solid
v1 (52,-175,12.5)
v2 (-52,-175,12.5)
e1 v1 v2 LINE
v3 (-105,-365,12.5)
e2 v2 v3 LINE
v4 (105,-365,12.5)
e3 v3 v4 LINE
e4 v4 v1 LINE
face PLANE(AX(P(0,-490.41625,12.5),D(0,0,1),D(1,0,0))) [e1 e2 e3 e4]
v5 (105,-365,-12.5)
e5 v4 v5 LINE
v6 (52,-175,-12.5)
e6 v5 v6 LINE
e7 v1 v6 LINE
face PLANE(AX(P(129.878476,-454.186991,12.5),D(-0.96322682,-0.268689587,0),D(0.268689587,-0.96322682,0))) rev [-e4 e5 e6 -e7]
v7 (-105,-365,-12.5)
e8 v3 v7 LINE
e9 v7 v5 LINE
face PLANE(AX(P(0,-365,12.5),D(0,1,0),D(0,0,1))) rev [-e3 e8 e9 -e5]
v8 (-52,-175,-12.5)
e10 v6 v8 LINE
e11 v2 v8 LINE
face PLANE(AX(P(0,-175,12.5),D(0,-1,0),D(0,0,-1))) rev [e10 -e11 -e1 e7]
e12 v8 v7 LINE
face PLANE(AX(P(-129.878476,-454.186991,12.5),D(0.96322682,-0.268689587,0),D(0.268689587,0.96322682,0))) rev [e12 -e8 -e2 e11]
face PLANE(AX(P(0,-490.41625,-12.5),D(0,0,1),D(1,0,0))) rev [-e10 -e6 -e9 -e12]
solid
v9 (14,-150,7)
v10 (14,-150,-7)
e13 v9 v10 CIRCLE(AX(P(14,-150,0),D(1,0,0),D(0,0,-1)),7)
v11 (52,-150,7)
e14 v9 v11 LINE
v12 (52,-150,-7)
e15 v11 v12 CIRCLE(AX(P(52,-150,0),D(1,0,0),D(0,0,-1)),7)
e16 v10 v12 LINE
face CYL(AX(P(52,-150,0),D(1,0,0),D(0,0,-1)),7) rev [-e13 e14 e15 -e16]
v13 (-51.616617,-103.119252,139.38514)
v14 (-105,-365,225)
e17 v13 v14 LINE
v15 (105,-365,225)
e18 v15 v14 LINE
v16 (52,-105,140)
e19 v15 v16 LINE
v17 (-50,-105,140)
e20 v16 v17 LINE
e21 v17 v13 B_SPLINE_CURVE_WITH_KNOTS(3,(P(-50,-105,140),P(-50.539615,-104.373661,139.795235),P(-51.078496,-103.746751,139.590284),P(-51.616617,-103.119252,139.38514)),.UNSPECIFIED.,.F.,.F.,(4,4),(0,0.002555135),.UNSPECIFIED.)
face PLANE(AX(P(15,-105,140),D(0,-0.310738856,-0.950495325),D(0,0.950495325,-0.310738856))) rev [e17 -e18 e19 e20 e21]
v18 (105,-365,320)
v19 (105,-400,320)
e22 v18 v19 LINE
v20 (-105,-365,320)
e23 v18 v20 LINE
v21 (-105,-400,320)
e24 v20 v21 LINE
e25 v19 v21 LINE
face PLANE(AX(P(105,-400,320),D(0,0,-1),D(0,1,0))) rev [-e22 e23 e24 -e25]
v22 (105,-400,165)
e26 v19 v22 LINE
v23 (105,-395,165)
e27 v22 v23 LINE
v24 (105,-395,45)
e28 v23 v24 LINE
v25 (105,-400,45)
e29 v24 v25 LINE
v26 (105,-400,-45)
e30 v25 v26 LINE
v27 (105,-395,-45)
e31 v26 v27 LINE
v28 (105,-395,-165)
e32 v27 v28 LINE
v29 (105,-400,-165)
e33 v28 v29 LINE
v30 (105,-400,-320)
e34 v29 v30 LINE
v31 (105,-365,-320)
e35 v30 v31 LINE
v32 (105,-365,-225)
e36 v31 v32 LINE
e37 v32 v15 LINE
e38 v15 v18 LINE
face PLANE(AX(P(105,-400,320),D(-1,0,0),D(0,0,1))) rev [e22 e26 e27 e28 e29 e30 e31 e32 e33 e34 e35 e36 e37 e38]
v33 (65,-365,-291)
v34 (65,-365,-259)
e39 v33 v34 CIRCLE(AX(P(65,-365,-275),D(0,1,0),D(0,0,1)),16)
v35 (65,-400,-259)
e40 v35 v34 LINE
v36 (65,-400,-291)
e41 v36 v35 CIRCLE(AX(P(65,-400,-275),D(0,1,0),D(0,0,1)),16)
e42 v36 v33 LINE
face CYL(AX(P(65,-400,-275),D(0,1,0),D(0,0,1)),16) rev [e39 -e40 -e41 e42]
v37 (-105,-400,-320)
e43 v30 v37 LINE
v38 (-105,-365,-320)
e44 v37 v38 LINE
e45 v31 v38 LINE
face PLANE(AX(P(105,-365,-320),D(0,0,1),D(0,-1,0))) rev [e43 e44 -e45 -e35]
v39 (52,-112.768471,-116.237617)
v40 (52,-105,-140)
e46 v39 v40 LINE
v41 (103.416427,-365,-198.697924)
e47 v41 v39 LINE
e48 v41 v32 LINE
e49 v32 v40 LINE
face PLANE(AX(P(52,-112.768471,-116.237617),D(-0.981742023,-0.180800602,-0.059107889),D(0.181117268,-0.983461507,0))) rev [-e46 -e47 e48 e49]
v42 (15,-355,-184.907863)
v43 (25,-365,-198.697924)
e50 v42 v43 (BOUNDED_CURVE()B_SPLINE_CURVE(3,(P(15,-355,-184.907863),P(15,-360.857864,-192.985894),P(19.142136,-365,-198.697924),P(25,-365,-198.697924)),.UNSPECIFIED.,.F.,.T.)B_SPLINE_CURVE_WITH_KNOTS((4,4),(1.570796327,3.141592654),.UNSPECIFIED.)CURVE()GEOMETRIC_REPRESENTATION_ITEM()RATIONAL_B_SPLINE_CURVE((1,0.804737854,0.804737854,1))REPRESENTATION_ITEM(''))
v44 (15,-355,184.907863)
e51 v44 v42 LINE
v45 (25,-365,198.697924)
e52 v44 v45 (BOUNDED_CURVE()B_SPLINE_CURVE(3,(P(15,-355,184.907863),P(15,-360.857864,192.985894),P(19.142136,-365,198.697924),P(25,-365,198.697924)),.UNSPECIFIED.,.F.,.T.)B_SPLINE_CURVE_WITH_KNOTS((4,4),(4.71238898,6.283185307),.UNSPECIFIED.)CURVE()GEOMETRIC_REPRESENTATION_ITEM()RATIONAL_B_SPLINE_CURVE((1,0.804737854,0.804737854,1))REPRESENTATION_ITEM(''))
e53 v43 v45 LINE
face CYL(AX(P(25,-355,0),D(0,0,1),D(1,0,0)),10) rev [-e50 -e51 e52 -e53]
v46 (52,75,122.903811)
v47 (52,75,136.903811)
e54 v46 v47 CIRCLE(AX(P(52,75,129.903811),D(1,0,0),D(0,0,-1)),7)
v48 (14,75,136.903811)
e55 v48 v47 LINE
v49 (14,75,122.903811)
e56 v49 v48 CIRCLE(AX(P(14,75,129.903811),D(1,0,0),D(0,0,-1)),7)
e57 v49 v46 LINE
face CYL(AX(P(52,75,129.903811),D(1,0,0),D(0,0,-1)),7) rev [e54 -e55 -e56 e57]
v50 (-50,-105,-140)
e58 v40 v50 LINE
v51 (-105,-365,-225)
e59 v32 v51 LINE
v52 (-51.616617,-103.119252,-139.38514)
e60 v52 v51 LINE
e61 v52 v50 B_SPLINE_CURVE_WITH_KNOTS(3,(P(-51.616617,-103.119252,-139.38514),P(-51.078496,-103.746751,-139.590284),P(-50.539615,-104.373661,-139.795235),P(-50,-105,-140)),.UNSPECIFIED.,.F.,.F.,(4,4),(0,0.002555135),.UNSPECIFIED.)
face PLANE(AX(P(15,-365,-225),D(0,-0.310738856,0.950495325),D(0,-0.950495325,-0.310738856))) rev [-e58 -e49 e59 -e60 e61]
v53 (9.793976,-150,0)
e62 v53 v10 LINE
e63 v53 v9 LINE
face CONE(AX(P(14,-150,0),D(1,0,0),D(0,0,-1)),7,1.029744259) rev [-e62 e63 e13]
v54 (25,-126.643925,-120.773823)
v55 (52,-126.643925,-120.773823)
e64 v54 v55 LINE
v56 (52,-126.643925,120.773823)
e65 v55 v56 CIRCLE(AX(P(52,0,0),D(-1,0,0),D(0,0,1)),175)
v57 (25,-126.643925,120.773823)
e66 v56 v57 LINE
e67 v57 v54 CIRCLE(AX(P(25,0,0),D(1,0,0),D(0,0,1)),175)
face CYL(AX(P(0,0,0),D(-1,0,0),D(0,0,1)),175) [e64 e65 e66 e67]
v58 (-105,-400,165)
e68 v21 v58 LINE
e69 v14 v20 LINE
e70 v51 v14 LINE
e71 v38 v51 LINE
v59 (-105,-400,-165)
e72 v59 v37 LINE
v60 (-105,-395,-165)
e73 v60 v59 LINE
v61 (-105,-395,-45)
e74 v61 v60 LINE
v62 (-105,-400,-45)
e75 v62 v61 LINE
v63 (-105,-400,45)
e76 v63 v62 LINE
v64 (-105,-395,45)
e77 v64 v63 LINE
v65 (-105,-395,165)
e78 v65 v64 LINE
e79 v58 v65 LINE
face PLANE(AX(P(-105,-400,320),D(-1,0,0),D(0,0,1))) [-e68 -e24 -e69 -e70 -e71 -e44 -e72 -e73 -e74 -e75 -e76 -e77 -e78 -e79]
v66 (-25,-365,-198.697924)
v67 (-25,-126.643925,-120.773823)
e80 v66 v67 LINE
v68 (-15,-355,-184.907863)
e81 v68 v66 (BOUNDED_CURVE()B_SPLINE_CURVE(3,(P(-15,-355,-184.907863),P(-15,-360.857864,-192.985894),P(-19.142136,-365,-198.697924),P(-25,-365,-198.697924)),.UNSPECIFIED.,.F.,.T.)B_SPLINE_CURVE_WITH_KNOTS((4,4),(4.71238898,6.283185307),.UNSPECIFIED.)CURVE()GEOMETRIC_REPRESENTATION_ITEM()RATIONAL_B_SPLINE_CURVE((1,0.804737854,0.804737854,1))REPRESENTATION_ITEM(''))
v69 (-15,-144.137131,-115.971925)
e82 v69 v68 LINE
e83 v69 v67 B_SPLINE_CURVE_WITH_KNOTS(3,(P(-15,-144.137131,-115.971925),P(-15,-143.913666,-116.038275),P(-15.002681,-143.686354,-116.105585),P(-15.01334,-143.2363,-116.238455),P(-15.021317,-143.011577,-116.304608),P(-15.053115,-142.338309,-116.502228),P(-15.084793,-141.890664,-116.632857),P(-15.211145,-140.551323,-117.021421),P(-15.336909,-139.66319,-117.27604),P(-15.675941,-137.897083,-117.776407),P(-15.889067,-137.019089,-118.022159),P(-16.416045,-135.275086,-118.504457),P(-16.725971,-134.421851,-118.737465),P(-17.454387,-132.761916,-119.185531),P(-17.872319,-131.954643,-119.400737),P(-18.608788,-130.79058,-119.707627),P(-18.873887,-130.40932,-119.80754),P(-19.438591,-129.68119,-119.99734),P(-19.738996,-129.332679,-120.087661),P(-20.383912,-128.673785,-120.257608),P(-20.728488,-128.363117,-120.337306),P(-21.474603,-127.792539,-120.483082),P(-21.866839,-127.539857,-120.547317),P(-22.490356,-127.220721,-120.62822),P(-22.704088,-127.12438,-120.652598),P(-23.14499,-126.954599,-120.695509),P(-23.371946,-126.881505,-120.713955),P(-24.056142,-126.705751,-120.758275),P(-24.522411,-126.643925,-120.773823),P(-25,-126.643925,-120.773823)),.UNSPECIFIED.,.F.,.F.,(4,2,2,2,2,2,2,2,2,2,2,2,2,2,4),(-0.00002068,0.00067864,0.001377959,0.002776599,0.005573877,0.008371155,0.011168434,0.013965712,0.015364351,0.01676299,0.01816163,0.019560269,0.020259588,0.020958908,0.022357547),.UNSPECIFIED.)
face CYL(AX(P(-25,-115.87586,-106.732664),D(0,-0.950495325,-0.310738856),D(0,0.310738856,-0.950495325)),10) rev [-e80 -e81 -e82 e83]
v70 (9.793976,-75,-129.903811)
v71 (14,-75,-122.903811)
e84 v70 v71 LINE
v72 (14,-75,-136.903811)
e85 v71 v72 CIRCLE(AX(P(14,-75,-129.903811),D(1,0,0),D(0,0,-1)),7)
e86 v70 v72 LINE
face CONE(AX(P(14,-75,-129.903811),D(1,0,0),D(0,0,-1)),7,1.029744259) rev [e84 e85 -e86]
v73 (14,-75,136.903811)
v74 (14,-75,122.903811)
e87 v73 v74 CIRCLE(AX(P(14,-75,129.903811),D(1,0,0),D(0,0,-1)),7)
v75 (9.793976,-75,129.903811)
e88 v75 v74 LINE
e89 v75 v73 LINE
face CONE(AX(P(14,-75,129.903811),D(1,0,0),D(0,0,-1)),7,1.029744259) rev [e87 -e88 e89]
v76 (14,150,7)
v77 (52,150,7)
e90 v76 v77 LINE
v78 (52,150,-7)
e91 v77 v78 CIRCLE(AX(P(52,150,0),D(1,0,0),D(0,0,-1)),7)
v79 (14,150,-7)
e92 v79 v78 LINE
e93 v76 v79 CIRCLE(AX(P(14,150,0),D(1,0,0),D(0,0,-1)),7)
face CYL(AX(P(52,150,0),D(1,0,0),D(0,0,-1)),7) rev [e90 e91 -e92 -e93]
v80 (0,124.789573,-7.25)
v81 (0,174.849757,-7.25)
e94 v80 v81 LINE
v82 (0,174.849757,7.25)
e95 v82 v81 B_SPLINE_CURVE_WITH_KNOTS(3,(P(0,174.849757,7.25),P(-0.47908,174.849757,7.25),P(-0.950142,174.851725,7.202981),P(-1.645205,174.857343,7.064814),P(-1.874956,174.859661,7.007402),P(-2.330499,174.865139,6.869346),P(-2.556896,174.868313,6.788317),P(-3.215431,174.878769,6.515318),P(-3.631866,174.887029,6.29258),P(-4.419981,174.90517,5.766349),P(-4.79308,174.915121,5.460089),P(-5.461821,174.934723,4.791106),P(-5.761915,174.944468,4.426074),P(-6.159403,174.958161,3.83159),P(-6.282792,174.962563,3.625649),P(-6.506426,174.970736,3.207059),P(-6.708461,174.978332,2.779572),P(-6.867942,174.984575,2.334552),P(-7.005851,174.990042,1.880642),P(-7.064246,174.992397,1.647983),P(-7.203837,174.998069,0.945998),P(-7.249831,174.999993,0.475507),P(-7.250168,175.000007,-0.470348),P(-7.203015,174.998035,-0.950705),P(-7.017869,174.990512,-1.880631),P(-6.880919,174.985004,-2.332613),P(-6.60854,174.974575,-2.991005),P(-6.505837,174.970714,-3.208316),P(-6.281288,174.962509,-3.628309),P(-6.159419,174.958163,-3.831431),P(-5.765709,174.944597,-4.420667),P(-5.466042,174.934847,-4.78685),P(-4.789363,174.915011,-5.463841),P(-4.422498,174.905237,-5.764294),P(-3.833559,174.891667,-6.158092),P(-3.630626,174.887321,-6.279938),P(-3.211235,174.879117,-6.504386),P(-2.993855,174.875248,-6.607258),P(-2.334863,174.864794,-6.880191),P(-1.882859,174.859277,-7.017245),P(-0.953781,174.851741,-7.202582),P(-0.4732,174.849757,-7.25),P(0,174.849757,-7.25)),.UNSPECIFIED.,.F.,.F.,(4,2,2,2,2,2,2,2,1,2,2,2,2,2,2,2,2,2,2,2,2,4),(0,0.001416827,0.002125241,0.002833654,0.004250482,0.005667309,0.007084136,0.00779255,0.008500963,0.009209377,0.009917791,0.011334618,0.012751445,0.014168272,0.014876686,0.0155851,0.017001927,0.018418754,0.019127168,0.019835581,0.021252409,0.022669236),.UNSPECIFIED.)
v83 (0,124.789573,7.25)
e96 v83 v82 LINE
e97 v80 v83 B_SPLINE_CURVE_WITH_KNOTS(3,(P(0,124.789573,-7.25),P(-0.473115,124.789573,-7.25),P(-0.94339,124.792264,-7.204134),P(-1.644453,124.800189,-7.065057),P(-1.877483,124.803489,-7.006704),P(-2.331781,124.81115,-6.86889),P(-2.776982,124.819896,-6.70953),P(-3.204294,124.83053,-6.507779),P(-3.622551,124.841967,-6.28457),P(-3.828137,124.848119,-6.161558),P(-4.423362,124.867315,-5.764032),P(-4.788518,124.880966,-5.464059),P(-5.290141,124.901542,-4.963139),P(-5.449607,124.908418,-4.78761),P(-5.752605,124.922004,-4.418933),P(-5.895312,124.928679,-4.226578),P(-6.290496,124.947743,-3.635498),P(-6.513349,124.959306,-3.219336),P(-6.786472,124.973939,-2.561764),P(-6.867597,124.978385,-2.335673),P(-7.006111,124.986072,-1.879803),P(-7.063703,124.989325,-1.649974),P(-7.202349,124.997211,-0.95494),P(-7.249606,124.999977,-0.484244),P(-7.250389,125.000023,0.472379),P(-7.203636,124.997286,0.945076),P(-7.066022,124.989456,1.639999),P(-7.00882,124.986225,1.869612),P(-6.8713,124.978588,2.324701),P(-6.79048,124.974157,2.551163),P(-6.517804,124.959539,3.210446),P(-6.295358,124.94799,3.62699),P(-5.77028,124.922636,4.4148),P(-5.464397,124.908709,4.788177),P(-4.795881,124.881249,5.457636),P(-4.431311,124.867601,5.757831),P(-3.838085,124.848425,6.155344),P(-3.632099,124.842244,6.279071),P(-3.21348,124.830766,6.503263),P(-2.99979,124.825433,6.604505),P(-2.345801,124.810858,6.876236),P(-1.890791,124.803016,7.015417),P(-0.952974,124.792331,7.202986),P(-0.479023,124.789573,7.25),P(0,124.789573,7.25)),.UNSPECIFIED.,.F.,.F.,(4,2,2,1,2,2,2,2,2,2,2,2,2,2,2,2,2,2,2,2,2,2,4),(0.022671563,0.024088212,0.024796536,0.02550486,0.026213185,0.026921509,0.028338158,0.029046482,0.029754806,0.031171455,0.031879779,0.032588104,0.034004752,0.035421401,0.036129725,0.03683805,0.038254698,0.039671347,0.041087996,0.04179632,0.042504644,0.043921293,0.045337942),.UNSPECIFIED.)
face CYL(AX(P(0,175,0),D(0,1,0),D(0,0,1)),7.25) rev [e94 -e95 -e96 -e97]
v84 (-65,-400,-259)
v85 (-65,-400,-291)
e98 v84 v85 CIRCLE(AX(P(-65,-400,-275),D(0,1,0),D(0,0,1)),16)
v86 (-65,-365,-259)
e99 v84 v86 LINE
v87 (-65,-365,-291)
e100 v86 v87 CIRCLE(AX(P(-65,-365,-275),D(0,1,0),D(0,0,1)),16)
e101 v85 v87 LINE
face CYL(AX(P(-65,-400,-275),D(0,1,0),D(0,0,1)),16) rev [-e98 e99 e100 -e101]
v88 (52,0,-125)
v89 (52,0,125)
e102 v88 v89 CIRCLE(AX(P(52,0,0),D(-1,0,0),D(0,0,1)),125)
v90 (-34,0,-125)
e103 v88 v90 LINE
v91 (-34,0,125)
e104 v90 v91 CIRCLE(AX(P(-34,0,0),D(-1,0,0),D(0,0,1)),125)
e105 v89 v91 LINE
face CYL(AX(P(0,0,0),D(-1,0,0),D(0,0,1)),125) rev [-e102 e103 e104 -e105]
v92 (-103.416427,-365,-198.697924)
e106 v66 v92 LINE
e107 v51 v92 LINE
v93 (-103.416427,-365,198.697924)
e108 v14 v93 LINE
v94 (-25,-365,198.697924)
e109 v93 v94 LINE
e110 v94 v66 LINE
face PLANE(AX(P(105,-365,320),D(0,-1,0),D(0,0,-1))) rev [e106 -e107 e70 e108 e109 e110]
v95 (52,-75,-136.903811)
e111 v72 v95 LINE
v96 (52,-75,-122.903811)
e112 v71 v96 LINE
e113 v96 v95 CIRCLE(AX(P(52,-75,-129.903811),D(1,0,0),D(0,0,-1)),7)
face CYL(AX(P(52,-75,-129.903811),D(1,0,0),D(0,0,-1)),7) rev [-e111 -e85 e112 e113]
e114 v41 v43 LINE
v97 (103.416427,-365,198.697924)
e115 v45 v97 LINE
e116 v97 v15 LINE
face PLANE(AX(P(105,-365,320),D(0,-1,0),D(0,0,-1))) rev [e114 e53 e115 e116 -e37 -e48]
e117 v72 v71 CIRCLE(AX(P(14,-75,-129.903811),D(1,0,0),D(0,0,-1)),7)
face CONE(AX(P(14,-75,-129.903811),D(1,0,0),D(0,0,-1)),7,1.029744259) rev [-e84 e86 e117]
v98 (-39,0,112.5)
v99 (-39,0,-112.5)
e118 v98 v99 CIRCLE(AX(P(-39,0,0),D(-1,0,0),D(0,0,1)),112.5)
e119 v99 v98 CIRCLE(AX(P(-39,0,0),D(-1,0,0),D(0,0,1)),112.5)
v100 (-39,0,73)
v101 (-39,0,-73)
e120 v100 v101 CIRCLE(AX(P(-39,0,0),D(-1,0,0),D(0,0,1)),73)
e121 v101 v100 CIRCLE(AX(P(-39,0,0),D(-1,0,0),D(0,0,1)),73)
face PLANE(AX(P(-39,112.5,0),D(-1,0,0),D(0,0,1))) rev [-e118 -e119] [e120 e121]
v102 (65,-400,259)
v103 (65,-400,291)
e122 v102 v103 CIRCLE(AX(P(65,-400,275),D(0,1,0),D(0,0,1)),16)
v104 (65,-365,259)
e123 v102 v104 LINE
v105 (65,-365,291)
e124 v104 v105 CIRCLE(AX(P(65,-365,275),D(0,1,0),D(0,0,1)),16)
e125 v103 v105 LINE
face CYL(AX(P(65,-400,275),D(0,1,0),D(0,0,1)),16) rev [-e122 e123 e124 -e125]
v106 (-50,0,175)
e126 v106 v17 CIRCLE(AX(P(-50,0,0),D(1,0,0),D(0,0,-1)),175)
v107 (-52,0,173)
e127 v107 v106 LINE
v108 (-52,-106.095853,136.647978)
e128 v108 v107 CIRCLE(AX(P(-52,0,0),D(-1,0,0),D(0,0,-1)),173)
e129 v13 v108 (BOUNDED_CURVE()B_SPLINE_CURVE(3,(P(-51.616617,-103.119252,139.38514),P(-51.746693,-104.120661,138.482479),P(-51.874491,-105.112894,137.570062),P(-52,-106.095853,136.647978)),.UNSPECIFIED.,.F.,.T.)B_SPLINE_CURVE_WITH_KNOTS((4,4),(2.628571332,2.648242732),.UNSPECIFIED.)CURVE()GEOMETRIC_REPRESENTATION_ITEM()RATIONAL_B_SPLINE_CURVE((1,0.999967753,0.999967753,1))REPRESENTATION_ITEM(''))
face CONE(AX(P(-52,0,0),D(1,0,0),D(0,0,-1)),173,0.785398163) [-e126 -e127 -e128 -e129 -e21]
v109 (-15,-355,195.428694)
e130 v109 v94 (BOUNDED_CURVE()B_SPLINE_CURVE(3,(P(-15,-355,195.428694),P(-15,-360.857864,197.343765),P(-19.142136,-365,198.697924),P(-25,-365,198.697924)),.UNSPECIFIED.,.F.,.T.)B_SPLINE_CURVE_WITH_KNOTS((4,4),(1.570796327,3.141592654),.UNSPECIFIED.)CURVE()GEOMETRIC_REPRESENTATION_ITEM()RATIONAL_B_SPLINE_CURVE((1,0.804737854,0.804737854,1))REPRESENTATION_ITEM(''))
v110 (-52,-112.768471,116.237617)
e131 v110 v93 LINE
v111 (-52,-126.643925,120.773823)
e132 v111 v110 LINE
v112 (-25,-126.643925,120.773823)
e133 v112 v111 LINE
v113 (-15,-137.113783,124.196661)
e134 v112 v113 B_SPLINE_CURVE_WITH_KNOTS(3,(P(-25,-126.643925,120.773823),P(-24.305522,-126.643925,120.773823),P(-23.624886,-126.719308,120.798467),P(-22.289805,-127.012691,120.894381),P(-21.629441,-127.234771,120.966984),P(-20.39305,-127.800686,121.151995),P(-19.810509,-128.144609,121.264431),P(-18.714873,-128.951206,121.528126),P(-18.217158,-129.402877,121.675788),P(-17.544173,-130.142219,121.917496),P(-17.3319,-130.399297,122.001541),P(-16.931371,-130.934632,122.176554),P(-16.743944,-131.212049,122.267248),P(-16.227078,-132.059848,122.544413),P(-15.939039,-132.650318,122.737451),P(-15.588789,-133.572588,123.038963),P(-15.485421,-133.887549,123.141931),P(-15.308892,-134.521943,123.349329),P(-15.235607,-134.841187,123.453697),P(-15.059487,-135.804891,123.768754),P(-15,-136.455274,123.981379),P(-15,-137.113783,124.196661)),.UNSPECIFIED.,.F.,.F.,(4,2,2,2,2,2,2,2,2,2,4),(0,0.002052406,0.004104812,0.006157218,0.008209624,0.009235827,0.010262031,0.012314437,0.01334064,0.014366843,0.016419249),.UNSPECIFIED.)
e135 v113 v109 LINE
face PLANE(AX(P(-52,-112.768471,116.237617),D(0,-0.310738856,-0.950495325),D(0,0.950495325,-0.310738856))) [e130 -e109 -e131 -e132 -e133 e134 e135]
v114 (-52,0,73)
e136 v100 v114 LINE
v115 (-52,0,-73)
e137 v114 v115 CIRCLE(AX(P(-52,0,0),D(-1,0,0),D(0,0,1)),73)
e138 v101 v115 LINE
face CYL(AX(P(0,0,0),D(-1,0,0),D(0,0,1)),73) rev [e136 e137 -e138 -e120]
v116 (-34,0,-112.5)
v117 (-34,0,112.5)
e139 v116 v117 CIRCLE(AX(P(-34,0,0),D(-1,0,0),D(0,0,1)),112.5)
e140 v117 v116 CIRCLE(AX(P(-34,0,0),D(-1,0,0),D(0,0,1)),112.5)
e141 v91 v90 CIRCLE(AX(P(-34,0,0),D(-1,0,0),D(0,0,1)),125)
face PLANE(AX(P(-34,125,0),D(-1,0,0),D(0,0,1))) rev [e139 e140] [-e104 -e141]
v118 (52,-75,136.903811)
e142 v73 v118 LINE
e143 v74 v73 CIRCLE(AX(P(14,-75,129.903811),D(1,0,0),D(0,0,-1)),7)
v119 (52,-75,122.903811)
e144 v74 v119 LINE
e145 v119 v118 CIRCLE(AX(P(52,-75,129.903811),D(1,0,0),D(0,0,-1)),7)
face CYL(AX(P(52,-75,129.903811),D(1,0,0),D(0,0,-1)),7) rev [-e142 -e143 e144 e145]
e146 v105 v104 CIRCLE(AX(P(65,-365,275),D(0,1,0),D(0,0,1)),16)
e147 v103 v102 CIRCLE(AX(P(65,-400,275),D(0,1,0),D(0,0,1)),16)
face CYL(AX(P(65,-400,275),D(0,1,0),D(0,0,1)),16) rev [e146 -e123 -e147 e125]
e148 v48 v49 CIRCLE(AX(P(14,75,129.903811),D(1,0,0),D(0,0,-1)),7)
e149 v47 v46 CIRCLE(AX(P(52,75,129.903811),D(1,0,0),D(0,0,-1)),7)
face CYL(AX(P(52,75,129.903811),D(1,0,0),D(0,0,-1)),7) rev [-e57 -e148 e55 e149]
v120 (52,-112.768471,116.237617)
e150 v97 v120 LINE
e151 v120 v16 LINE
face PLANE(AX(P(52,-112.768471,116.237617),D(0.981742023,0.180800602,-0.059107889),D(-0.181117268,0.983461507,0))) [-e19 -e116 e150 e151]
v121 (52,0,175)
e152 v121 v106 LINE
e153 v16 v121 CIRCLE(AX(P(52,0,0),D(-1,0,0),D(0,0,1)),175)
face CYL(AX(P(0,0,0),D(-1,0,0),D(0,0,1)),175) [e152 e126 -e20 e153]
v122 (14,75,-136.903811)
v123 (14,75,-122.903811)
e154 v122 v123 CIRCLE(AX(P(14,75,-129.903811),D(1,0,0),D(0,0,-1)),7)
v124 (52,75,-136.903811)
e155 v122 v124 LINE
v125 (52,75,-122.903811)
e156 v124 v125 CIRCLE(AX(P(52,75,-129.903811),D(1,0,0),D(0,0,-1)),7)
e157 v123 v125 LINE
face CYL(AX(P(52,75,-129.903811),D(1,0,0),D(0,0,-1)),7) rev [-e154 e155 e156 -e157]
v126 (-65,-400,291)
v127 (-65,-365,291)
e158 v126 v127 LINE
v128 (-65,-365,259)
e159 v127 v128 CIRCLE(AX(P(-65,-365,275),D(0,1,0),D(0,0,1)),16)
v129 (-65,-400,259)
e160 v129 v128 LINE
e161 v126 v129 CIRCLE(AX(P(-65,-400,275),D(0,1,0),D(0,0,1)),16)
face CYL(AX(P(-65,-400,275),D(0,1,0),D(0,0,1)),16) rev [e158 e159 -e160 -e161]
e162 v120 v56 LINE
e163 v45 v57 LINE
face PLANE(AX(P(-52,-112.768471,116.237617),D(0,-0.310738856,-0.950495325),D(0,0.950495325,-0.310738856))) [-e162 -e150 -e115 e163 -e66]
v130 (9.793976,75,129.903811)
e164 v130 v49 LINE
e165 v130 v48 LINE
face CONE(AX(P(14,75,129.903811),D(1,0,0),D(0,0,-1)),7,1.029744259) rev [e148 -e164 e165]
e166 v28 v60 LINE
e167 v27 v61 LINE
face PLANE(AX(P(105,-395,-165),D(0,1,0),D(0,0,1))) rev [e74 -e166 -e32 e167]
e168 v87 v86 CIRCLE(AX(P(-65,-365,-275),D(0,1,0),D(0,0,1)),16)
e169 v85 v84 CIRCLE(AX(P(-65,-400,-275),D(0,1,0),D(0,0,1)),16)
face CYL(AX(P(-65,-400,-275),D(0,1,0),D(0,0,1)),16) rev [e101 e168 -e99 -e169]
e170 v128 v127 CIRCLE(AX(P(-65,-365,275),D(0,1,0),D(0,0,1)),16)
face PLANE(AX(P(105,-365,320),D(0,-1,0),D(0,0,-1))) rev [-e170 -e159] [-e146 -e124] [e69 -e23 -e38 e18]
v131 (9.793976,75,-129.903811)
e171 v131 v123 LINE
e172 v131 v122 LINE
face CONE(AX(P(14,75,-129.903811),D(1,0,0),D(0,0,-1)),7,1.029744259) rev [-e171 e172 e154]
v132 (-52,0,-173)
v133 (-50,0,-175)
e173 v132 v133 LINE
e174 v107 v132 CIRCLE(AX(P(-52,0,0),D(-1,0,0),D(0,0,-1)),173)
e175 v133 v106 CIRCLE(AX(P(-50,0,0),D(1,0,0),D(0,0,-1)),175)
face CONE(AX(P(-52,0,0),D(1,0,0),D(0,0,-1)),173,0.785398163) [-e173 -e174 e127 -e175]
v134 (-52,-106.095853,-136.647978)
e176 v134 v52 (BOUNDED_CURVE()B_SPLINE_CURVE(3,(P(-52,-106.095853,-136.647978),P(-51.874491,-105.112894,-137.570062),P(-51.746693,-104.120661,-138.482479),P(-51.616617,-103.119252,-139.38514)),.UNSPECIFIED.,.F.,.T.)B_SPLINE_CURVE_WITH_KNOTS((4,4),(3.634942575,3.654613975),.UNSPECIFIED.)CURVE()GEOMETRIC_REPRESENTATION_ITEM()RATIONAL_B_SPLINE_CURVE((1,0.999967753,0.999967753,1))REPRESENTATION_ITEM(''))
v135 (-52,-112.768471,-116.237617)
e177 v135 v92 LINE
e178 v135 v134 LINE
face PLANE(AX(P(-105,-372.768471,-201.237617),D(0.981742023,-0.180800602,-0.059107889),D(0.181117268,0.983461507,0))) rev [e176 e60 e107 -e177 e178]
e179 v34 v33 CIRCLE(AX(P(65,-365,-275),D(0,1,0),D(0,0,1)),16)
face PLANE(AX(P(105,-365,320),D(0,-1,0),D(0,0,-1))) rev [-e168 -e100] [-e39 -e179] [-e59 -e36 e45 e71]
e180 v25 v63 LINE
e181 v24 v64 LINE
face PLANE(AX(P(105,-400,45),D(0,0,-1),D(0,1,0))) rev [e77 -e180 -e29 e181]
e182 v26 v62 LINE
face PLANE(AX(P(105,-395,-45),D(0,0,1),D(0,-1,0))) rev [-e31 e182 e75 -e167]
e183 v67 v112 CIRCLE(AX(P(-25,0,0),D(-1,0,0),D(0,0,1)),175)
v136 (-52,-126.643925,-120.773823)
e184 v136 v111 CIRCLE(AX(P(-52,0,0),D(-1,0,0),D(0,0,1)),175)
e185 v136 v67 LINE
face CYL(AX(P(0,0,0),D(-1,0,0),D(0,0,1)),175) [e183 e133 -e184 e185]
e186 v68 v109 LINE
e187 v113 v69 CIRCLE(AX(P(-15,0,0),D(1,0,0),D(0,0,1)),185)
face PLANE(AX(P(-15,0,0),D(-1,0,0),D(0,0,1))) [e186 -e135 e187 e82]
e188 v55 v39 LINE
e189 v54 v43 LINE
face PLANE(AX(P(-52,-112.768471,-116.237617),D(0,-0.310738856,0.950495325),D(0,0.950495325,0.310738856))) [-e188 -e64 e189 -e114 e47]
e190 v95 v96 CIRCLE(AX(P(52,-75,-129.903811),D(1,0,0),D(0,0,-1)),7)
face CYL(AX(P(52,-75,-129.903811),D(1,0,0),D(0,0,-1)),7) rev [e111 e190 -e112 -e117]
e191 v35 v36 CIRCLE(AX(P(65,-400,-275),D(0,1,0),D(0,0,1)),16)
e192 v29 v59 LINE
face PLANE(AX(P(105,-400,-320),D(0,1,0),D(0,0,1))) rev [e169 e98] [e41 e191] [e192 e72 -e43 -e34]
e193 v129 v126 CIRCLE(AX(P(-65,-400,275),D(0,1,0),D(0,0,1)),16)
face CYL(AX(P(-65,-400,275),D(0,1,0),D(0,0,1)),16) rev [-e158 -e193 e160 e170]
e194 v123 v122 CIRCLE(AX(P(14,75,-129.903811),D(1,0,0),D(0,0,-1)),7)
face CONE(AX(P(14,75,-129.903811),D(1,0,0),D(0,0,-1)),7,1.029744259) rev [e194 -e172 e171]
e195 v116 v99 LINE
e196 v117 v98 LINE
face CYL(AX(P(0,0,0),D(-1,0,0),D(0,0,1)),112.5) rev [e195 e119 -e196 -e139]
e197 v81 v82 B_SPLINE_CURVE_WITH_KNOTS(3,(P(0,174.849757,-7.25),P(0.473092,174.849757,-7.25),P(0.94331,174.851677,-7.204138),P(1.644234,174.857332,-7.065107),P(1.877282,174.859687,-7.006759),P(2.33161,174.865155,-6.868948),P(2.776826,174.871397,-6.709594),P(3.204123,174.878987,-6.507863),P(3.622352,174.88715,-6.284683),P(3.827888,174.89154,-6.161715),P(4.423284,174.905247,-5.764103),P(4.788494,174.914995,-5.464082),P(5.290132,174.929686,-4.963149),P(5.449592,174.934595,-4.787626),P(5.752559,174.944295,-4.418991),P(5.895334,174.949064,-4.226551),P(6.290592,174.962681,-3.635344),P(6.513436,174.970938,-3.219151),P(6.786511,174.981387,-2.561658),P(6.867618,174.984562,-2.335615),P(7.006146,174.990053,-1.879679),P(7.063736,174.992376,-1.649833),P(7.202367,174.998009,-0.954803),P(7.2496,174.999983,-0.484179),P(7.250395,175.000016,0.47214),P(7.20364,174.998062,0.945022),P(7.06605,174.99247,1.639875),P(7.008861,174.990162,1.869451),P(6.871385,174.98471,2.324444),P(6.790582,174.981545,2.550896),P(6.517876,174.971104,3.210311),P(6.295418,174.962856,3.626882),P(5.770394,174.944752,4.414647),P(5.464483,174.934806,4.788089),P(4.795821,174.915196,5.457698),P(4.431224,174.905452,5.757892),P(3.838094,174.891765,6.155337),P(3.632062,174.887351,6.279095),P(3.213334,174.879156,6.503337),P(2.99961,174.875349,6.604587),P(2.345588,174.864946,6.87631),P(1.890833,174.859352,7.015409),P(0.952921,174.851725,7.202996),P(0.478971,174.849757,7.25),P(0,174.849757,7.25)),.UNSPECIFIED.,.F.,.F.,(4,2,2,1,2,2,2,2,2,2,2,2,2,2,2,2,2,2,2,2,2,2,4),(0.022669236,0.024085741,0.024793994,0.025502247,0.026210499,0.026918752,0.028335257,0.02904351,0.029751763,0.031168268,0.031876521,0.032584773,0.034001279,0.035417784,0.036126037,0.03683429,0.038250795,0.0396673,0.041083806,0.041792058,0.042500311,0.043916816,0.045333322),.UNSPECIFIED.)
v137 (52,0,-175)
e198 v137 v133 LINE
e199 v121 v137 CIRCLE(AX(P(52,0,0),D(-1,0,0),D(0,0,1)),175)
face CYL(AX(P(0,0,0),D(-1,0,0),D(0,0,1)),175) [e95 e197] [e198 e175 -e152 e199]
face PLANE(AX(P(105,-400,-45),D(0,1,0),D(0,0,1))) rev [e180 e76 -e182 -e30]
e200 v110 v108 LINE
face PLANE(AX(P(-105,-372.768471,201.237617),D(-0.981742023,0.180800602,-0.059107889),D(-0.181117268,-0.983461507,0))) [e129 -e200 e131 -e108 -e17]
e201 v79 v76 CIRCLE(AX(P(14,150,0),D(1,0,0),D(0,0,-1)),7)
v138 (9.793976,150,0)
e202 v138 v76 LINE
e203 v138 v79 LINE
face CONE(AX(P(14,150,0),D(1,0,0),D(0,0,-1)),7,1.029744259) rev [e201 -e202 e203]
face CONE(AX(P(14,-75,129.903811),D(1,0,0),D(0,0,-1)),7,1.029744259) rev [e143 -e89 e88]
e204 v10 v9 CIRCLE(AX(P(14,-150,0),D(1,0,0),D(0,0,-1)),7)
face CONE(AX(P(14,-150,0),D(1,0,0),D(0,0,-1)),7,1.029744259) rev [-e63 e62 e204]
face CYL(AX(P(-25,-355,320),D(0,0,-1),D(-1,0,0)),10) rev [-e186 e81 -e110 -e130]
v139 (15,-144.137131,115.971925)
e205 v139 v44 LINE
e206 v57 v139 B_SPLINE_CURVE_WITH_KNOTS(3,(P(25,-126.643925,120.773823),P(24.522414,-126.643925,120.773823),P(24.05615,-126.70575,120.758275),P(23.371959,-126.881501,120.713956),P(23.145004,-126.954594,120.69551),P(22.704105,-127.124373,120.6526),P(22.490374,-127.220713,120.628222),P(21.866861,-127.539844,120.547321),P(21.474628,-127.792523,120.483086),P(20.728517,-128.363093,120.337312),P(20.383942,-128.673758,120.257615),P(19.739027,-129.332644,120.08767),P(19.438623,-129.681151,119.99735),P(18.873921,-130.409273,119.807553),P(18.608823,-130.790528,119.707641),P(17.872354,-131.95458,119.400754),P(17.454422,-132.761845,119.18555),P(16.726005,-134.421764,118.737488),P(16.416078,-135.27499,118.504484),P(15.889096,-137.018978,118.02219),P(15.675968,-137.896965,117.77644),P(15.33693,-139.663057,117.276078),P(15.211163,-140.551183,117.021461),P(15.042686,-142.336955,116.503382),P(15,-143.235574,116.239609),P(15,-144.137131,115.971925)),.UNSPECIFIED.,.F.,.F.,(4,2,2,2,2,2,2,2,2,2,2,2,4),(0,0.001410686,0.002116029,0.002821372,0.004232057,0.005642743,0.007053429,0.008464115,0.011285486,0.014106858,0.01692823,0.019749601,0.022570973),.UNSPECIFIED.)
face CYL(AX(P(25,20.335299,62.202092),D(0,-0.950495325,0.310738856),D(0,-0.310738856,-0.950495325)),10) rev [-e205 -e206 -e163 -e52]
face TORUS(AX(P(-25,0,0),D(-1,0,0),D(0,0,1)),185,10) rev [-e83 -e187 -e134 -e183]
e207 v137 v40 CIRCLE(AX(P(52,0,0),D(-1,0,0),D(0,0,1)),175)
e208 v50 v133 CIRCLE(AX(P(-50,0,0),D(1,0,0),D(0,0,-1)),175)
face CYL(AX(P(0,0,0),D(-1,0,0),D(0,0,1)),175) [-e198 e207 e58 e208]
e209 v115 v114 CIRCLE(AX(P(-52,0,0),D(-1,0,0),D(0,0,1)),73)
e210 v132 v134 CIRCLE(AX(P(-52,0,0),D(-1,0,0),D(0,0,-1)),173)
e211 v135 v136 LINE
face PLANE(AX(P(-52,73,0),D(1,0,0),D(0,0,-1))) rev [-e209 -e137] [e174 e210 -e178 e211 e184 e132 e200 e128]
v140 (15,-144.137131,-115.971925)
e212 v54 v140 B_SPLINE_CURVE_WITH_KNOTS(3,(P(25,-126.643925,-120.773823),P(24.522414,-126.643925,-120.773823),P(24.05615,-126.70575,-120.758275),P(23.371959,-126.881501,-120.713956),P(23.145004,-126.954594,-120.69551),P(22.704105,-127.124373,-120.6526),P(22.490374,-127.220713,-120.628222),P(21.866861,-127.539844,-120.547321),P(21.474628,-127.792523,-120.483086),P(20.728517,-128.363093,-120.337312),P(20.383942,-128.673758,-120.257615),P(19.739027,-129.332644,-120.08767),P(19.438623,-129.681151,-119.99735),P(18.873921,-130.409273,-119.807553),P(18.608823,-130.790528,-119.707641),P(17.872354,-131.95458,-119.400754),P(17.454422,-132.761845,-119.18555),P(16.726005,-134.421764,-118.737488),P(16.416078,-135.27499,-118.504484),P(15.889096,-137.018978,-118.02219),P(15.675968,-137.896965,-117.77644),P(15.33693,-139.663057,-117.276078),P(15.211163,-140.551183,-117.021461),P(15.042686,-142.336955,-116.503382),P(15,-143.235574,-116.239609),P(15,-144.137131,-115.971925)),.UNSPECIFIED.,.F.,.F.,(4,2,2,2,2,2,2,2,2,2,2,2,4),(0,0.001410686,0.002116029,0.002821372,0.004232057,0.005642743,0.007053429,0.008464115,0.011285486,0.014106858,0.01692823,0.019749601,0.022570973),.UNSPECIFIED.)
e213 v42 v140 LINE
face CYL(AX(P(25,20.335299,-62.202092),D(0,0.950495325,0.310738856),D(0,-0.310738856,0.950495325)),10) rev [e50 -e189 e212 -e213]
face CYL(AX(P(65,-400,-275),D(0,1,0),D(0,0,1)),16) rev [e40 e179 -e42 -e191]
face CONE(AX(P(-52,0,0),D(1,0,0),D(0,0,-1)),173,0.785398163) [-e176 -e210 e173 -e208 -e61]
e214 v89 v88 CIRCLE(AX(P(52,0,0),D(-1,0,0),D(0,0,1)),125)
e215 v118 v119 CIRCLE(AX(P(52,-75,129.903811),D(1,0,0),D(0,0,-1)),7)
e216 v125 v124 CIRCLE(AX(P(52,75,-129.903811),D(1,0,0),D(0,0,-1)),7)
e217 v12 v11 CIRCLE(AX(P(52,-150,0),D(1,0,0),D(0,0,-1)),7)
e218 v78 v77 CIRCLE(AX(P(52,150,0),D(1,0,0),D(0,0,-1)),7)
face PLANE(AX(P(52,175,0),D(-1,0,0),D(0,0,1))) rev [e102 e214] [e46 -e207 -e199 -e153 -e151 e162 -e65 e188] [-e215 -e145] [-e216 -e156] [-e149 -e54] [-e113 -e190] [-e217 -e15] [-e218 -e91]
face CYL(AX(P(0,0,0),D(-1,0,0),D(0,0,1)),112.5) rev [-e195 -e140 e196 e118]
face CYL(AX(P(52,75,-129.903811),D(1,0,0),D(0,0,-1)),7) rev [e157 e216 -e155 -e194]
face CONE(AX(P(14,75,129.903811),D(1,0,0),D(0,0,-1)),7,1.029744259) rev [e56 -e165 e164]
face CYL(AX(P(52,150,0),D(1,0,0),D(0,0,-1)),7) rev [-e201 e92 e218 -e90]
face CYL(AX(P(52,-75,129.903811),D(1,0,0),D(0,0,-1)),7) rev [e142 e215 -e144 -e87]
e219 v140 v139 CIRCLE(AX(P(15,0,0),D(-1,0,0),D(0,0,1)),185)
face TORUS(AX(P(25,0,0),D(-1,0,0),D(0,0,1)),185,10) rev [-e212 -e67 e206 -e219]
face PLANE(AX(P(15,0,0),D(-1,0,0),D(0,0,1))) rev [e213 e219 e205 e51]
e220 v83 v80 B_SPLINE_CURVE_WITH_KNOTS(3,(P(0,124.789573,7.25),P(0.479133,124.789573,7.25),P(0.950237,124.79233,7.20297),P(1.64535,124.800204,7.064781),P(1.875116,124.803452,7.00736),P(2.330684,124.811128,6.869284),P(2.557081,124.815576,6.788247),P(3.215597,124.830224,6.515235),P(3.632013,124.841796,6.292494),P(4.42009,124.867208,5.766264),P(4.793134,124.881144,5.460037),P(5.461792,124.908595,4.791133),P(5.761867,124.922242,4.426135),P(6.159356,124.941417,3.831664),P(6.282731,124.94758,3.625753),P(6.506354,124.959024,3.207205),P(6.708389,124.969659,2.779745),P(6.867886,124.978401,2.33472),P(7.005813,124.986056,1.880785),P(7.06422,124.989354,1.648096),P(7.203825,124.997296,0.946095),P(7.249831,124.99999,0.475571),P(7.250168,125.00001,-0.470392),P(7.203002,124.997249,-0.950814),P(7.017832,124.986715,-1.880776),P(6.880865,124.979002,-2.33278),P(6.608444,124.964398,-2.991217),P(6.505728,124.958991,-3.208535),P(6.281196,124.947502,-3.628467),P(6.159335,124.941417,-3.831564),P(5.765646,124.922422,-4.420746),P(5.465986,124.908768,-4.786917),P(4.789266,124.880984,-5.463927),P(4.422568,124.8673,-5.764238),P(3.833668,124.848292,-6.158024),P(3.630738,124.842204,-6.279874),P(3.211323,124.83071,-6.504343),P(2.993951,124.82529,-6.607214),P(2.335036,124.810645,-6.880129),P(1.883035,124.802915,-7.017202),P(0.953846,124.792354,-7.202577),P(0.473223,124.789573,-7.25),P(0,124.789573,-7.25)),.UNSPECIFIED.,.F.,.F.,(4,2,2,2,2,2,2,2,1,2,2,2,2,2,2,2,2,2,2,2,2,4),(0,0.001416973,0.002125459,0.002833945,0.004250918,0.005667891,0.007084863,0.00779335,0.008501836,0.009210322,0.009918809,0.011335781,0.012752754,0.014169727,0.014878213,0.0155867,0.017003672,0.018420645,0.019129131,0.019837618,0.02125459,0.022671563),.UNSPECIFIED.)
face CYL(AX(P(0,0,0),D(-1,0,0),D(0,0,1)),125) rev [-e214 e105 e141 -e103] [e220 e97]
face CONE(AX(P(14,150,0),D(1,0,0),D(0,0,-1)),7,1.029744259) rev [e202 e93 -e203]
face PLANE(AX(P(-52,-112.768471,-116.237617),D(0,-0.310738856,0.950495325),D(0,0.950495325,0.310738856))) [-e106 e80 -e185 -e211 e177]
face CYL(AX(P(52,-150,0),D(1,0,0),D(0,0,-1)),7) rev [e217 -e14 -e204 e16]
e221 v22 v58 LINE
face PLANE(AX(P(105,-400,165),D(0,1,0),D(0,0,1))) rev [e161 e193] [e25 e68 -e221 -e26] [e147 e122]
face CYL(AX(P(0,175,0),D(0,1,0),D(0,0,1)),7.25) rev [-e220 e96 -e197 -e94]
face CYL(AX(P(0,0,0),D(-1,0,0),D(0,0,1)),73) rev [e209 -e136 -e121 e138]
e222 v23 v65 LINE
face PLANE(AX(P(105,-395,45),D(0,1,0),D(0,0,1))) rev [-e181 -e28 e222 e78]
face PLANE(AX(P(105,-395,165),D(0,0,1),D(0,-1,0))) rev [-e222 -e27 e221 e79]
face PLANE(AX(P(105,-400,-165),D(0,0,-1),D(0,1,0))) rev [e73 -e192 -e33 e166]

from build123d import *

# Parameters (mm, degrees)
BOSS_EXTRUDE1_DEPTH         = 105
BOSS_EXTRUDE2_DEPTH         = 15
BOSS_EXTRUDE6_DEPTH         = 12.5
BOSS_EXTRUDE3_DEPTH         = 25
FILLET1_R                   = 10
SKETCH7_R                   = 16
CUT_EXTRUDE1_DEPTH          = 637.41574462
M16_TAPPED_HOLE1_AT_2_COUNT = 2
M16_TAPPED_HOLE1_AT_2_PITCH = 150
M16_TAPPED_HOLE1_AT_3_COUNT = 2
M16_TAPPED_HOLE1_AT_3_PITCH = 259.807621135
M16_TAPPED_HOLE1_AT_4_COUNT = 2
M16_TAPPED_HOLE1_AT_4_PITCH = 300
M16_TAPPED_HOLE1_AT_5_COUNT = 2
M16_TAPPED_HOLE1_AT_5_PITCH = 259.807621135
M16_TAPPED_HOLE1_AT_6_COUNT = 2
M16_TAPPED_HOLE1_AT_6_PITCH = 150
CHAMFER1_SIZE               = 2


with BuildPart() as part:
    # Sketch1 → Revolve1 (revolve)
    with BuildSketch(Plane.XY, mode=Mode.PRIVATE) as revolve1_sk:
        Polygon((-52, 73), (-52, 175), (52, 175), (52, 125), (-34, 125), (-34, 112.5), (-39, 112.5), (-39, 73), align=None)
    revolve(revolve1_sk.sketch.rotate(Axis((0, 0, 0), (1, 0, 0)), 90), axis=Axis((0, 0, 0), (1, 0, 0)))



with BuildPart() as body_2:
    # Sketch2 → Boss-Extrude1 (new, symmetric)
    with BuildSketch(Plane(origin=(0, 0, 0), x_dir=(0, 0, -1), z_dir=(1, 0, 0))):
        Polygon((-320, -400), (-320, -365), (320, -365), (320, -400), (165, -400), (165, -395), (45, -395), (45, -400), (-45, -400), (-45, -395), (-165, -395), (-165, -400), align=None)
    extrude(amount=BOSS_EXTRUDE1_DEPTH, both=True)


with BuildPart() as part_1:
    add(part.part)

    add(body_2.part)  # Boss-Extrude2 merges body 2
    # Sketch3 → Boss-Extrude2 (add, symmetric)
    with BuildSketch(Plane(origin=(0, 0, 0), x_dir=(0, 0, -1), z_dir=(1, 0, 0))):
        with BuildLine():
            Line((-140, -105), (-225, -365))
            Line((-225, -365), (225, -365))
            Line((225, -365), (140, -105))
            ThreePointArc((140, -105), (0, -175), (-140, -105))
        make_face()
    extrude(amount=BOSS_EXTRUDE2_DEPTH, both=True)

    # Sketch4 → Boss-Extrude3 (add)
    with BuildSketch(Plane(origin=(0, 31.211159372, 95.469428667), x_dir=(1, 0, 0), z_dir=(0, 0.3107388563074221, 0.9504953251756451))):
        Polygon((-52, -143.305449026), (52, -143.305449026), (105, -416.847036358), (-105, -416.847036358), align=None)
    boss_extrude3 = extrude(amount=-BOSS_EXTRUDE3_DEPTH)

    # Mirror1: Boss-Extrude3 across plane
    add(boss_extrude3.mirror(Plane.XY))

    # Fillet1
    fillet1_edges = [part_1.edges().sort_by_distance(p)[0] for p in [
        (15, -365, 0),
        (-15, -365, 0),
        (15, -245.821962461, 159.735873561),
        (-15, -175, 0),
        (15, -175, 0),
        (-15, -245.821962461, -159.735873561),
        (15, -245.821962461, -159.735873561),
    ]]
    fillet(fillet1_edges, radius=FILLET1_R)

    # Sketch7 → Cut-Extrude1 (cut, through all)
    with BuildSketch(Plane(origin=(0, -365, 0), x_dir=(1, 0, 0), z_dir=(0, 1, 0))):
        with Locations(Location((-65, 275, 0), (0, 0, 270))):
            Circle(SKETCH7_R)
        with Locations(Location((65, 275, 0), (0, 0, 270))):
            Circle(SKETCH7_R)
        with Locations(Location((-65, -275, 0), (0, 0, 270))):
            Circle(SKETCH7_R)
        with Locations(Location((65, -275, 0), (0, 0, 270))):
            Circle(SKETCH7_R)
    extrude(amount=-CUT_EXTRUDE1_DEPTH, mode=Mode.SUBTRACT)

    # Sketch9 → M16 Tapped Hole1 (revolve, cut)
    with BuildSketch(Plane(origin=(52, -75, 129.903810568), x_dir=(0, 0, -1), z_dir=(0, 1, 0))):
        Polygon((0, 0), (0, 42.206024333), (7, 38), (7, 0), align=None)
    m16_tapped_hole1 = revolve(axis=Axis((58.35, -75, 129.903810568), (-1, 0, 0)), mode=Mode.SUBTRACT)

    # M16 Tapped Hole1 at 2: M16 Tapped Hole1 ×2
    with Locations(*[Vector(0, -0.5000000000000074, -0.8660254037844345) * (i * M16_TAPPED_HOLE1_AT_2_PITCH) for i in range(1, M16_TAPPED_HOLE1_AT_2_COUNT)]):
        add(m16_tapped_hole1, mode=Mode.SUBTRACT)

    # M16 Tapped Hole1 at 3: M16 Tapped Hole1 ×2
    with Locations(*[(0, 0, -i * M16_TAPPED_HOLE1_AT_3_PITCH) for i in range(1, M16_TAPPED_HOLE1_AT_3_COUNT)]):
        add(m16_tapped_hole1, mode=Mode.SUBTRACT)

    # M16 Tapped Hole1 at 4: M16 Tapped Hole1 ×2
    with Locations(*[Vector(0, 0.499999999999996, -0.8660254037844409) * (i * M16_TAPPED_HOLE1_AT_4_PITCH) for i in range(1, M16_TAPPED_HOLE1_AT_4_COUNT)]):
        add(m16_tapped_hole1, mode=Mode.SUBTRACT)

    # M16 Tapped Hole1 at 5: M16 Tapped Hole1 ×2
    with Locations(*[Vector(0, 0.8660254037844365, -0.5000000000000039) * (i * M16_TAPPED_HOLE1_AT_5_PITCH) for i in range(1, M16_TAPPED_HOLE1_AT_5_COUNT)]):
        add(m16_tapped_hole1, mode=Mode.SUBTRACT)

    # M16 Tapped Hole1 at 6: M16 Tapped Hole1 ×2
    with Locations(*[(0, i * M16_TAPPED_HOLE1_AT_6_PITCH, 0) for i in range(1, M16_TAPPED_HOLE1_AT_6_COUNT)]):
        add(m16_tapped_hole1, mode=Mode.SUBTRACT)

    # Sketch12 → M16x1.5 Tapped Hole1 (revolve, cut)
    with BuildSketch(Plane(origin=(0, 175, 0), x_dir=(0, 0, 1), z_dir=(1, 0, 0))):
        Polygon((0, 0), (0, 60.856239488), (7.25, 56.5), (7.25, 0), align=None)
    revolve(axis=Axis((0, 181.35, 0), (0, -1, 0)), mode=Mode.SUBTRACT)

    # Chamfer1
    chamfer1_edges = [part_1.edges().sort_by_distance(p)[0] for p in [
        (-52, 175, 0),
    ]]
    chamfer(chamfer1_edges, length=CHAMFER1_SIZE)


with BuildPart() as body_2_2:
    # Sketch6 → Boss-Extrude6 (new, symmetric)
    with BuildSketch(Plane.XY):
        Polygon((105, -365), (52, -175), (-52, -175), (-105, -365), align=None)
    extrude(amount=BOSS_EXTRUDE6_DEPTH, both=True)


solid = Compound([part_1.part, body_2_2.part])
